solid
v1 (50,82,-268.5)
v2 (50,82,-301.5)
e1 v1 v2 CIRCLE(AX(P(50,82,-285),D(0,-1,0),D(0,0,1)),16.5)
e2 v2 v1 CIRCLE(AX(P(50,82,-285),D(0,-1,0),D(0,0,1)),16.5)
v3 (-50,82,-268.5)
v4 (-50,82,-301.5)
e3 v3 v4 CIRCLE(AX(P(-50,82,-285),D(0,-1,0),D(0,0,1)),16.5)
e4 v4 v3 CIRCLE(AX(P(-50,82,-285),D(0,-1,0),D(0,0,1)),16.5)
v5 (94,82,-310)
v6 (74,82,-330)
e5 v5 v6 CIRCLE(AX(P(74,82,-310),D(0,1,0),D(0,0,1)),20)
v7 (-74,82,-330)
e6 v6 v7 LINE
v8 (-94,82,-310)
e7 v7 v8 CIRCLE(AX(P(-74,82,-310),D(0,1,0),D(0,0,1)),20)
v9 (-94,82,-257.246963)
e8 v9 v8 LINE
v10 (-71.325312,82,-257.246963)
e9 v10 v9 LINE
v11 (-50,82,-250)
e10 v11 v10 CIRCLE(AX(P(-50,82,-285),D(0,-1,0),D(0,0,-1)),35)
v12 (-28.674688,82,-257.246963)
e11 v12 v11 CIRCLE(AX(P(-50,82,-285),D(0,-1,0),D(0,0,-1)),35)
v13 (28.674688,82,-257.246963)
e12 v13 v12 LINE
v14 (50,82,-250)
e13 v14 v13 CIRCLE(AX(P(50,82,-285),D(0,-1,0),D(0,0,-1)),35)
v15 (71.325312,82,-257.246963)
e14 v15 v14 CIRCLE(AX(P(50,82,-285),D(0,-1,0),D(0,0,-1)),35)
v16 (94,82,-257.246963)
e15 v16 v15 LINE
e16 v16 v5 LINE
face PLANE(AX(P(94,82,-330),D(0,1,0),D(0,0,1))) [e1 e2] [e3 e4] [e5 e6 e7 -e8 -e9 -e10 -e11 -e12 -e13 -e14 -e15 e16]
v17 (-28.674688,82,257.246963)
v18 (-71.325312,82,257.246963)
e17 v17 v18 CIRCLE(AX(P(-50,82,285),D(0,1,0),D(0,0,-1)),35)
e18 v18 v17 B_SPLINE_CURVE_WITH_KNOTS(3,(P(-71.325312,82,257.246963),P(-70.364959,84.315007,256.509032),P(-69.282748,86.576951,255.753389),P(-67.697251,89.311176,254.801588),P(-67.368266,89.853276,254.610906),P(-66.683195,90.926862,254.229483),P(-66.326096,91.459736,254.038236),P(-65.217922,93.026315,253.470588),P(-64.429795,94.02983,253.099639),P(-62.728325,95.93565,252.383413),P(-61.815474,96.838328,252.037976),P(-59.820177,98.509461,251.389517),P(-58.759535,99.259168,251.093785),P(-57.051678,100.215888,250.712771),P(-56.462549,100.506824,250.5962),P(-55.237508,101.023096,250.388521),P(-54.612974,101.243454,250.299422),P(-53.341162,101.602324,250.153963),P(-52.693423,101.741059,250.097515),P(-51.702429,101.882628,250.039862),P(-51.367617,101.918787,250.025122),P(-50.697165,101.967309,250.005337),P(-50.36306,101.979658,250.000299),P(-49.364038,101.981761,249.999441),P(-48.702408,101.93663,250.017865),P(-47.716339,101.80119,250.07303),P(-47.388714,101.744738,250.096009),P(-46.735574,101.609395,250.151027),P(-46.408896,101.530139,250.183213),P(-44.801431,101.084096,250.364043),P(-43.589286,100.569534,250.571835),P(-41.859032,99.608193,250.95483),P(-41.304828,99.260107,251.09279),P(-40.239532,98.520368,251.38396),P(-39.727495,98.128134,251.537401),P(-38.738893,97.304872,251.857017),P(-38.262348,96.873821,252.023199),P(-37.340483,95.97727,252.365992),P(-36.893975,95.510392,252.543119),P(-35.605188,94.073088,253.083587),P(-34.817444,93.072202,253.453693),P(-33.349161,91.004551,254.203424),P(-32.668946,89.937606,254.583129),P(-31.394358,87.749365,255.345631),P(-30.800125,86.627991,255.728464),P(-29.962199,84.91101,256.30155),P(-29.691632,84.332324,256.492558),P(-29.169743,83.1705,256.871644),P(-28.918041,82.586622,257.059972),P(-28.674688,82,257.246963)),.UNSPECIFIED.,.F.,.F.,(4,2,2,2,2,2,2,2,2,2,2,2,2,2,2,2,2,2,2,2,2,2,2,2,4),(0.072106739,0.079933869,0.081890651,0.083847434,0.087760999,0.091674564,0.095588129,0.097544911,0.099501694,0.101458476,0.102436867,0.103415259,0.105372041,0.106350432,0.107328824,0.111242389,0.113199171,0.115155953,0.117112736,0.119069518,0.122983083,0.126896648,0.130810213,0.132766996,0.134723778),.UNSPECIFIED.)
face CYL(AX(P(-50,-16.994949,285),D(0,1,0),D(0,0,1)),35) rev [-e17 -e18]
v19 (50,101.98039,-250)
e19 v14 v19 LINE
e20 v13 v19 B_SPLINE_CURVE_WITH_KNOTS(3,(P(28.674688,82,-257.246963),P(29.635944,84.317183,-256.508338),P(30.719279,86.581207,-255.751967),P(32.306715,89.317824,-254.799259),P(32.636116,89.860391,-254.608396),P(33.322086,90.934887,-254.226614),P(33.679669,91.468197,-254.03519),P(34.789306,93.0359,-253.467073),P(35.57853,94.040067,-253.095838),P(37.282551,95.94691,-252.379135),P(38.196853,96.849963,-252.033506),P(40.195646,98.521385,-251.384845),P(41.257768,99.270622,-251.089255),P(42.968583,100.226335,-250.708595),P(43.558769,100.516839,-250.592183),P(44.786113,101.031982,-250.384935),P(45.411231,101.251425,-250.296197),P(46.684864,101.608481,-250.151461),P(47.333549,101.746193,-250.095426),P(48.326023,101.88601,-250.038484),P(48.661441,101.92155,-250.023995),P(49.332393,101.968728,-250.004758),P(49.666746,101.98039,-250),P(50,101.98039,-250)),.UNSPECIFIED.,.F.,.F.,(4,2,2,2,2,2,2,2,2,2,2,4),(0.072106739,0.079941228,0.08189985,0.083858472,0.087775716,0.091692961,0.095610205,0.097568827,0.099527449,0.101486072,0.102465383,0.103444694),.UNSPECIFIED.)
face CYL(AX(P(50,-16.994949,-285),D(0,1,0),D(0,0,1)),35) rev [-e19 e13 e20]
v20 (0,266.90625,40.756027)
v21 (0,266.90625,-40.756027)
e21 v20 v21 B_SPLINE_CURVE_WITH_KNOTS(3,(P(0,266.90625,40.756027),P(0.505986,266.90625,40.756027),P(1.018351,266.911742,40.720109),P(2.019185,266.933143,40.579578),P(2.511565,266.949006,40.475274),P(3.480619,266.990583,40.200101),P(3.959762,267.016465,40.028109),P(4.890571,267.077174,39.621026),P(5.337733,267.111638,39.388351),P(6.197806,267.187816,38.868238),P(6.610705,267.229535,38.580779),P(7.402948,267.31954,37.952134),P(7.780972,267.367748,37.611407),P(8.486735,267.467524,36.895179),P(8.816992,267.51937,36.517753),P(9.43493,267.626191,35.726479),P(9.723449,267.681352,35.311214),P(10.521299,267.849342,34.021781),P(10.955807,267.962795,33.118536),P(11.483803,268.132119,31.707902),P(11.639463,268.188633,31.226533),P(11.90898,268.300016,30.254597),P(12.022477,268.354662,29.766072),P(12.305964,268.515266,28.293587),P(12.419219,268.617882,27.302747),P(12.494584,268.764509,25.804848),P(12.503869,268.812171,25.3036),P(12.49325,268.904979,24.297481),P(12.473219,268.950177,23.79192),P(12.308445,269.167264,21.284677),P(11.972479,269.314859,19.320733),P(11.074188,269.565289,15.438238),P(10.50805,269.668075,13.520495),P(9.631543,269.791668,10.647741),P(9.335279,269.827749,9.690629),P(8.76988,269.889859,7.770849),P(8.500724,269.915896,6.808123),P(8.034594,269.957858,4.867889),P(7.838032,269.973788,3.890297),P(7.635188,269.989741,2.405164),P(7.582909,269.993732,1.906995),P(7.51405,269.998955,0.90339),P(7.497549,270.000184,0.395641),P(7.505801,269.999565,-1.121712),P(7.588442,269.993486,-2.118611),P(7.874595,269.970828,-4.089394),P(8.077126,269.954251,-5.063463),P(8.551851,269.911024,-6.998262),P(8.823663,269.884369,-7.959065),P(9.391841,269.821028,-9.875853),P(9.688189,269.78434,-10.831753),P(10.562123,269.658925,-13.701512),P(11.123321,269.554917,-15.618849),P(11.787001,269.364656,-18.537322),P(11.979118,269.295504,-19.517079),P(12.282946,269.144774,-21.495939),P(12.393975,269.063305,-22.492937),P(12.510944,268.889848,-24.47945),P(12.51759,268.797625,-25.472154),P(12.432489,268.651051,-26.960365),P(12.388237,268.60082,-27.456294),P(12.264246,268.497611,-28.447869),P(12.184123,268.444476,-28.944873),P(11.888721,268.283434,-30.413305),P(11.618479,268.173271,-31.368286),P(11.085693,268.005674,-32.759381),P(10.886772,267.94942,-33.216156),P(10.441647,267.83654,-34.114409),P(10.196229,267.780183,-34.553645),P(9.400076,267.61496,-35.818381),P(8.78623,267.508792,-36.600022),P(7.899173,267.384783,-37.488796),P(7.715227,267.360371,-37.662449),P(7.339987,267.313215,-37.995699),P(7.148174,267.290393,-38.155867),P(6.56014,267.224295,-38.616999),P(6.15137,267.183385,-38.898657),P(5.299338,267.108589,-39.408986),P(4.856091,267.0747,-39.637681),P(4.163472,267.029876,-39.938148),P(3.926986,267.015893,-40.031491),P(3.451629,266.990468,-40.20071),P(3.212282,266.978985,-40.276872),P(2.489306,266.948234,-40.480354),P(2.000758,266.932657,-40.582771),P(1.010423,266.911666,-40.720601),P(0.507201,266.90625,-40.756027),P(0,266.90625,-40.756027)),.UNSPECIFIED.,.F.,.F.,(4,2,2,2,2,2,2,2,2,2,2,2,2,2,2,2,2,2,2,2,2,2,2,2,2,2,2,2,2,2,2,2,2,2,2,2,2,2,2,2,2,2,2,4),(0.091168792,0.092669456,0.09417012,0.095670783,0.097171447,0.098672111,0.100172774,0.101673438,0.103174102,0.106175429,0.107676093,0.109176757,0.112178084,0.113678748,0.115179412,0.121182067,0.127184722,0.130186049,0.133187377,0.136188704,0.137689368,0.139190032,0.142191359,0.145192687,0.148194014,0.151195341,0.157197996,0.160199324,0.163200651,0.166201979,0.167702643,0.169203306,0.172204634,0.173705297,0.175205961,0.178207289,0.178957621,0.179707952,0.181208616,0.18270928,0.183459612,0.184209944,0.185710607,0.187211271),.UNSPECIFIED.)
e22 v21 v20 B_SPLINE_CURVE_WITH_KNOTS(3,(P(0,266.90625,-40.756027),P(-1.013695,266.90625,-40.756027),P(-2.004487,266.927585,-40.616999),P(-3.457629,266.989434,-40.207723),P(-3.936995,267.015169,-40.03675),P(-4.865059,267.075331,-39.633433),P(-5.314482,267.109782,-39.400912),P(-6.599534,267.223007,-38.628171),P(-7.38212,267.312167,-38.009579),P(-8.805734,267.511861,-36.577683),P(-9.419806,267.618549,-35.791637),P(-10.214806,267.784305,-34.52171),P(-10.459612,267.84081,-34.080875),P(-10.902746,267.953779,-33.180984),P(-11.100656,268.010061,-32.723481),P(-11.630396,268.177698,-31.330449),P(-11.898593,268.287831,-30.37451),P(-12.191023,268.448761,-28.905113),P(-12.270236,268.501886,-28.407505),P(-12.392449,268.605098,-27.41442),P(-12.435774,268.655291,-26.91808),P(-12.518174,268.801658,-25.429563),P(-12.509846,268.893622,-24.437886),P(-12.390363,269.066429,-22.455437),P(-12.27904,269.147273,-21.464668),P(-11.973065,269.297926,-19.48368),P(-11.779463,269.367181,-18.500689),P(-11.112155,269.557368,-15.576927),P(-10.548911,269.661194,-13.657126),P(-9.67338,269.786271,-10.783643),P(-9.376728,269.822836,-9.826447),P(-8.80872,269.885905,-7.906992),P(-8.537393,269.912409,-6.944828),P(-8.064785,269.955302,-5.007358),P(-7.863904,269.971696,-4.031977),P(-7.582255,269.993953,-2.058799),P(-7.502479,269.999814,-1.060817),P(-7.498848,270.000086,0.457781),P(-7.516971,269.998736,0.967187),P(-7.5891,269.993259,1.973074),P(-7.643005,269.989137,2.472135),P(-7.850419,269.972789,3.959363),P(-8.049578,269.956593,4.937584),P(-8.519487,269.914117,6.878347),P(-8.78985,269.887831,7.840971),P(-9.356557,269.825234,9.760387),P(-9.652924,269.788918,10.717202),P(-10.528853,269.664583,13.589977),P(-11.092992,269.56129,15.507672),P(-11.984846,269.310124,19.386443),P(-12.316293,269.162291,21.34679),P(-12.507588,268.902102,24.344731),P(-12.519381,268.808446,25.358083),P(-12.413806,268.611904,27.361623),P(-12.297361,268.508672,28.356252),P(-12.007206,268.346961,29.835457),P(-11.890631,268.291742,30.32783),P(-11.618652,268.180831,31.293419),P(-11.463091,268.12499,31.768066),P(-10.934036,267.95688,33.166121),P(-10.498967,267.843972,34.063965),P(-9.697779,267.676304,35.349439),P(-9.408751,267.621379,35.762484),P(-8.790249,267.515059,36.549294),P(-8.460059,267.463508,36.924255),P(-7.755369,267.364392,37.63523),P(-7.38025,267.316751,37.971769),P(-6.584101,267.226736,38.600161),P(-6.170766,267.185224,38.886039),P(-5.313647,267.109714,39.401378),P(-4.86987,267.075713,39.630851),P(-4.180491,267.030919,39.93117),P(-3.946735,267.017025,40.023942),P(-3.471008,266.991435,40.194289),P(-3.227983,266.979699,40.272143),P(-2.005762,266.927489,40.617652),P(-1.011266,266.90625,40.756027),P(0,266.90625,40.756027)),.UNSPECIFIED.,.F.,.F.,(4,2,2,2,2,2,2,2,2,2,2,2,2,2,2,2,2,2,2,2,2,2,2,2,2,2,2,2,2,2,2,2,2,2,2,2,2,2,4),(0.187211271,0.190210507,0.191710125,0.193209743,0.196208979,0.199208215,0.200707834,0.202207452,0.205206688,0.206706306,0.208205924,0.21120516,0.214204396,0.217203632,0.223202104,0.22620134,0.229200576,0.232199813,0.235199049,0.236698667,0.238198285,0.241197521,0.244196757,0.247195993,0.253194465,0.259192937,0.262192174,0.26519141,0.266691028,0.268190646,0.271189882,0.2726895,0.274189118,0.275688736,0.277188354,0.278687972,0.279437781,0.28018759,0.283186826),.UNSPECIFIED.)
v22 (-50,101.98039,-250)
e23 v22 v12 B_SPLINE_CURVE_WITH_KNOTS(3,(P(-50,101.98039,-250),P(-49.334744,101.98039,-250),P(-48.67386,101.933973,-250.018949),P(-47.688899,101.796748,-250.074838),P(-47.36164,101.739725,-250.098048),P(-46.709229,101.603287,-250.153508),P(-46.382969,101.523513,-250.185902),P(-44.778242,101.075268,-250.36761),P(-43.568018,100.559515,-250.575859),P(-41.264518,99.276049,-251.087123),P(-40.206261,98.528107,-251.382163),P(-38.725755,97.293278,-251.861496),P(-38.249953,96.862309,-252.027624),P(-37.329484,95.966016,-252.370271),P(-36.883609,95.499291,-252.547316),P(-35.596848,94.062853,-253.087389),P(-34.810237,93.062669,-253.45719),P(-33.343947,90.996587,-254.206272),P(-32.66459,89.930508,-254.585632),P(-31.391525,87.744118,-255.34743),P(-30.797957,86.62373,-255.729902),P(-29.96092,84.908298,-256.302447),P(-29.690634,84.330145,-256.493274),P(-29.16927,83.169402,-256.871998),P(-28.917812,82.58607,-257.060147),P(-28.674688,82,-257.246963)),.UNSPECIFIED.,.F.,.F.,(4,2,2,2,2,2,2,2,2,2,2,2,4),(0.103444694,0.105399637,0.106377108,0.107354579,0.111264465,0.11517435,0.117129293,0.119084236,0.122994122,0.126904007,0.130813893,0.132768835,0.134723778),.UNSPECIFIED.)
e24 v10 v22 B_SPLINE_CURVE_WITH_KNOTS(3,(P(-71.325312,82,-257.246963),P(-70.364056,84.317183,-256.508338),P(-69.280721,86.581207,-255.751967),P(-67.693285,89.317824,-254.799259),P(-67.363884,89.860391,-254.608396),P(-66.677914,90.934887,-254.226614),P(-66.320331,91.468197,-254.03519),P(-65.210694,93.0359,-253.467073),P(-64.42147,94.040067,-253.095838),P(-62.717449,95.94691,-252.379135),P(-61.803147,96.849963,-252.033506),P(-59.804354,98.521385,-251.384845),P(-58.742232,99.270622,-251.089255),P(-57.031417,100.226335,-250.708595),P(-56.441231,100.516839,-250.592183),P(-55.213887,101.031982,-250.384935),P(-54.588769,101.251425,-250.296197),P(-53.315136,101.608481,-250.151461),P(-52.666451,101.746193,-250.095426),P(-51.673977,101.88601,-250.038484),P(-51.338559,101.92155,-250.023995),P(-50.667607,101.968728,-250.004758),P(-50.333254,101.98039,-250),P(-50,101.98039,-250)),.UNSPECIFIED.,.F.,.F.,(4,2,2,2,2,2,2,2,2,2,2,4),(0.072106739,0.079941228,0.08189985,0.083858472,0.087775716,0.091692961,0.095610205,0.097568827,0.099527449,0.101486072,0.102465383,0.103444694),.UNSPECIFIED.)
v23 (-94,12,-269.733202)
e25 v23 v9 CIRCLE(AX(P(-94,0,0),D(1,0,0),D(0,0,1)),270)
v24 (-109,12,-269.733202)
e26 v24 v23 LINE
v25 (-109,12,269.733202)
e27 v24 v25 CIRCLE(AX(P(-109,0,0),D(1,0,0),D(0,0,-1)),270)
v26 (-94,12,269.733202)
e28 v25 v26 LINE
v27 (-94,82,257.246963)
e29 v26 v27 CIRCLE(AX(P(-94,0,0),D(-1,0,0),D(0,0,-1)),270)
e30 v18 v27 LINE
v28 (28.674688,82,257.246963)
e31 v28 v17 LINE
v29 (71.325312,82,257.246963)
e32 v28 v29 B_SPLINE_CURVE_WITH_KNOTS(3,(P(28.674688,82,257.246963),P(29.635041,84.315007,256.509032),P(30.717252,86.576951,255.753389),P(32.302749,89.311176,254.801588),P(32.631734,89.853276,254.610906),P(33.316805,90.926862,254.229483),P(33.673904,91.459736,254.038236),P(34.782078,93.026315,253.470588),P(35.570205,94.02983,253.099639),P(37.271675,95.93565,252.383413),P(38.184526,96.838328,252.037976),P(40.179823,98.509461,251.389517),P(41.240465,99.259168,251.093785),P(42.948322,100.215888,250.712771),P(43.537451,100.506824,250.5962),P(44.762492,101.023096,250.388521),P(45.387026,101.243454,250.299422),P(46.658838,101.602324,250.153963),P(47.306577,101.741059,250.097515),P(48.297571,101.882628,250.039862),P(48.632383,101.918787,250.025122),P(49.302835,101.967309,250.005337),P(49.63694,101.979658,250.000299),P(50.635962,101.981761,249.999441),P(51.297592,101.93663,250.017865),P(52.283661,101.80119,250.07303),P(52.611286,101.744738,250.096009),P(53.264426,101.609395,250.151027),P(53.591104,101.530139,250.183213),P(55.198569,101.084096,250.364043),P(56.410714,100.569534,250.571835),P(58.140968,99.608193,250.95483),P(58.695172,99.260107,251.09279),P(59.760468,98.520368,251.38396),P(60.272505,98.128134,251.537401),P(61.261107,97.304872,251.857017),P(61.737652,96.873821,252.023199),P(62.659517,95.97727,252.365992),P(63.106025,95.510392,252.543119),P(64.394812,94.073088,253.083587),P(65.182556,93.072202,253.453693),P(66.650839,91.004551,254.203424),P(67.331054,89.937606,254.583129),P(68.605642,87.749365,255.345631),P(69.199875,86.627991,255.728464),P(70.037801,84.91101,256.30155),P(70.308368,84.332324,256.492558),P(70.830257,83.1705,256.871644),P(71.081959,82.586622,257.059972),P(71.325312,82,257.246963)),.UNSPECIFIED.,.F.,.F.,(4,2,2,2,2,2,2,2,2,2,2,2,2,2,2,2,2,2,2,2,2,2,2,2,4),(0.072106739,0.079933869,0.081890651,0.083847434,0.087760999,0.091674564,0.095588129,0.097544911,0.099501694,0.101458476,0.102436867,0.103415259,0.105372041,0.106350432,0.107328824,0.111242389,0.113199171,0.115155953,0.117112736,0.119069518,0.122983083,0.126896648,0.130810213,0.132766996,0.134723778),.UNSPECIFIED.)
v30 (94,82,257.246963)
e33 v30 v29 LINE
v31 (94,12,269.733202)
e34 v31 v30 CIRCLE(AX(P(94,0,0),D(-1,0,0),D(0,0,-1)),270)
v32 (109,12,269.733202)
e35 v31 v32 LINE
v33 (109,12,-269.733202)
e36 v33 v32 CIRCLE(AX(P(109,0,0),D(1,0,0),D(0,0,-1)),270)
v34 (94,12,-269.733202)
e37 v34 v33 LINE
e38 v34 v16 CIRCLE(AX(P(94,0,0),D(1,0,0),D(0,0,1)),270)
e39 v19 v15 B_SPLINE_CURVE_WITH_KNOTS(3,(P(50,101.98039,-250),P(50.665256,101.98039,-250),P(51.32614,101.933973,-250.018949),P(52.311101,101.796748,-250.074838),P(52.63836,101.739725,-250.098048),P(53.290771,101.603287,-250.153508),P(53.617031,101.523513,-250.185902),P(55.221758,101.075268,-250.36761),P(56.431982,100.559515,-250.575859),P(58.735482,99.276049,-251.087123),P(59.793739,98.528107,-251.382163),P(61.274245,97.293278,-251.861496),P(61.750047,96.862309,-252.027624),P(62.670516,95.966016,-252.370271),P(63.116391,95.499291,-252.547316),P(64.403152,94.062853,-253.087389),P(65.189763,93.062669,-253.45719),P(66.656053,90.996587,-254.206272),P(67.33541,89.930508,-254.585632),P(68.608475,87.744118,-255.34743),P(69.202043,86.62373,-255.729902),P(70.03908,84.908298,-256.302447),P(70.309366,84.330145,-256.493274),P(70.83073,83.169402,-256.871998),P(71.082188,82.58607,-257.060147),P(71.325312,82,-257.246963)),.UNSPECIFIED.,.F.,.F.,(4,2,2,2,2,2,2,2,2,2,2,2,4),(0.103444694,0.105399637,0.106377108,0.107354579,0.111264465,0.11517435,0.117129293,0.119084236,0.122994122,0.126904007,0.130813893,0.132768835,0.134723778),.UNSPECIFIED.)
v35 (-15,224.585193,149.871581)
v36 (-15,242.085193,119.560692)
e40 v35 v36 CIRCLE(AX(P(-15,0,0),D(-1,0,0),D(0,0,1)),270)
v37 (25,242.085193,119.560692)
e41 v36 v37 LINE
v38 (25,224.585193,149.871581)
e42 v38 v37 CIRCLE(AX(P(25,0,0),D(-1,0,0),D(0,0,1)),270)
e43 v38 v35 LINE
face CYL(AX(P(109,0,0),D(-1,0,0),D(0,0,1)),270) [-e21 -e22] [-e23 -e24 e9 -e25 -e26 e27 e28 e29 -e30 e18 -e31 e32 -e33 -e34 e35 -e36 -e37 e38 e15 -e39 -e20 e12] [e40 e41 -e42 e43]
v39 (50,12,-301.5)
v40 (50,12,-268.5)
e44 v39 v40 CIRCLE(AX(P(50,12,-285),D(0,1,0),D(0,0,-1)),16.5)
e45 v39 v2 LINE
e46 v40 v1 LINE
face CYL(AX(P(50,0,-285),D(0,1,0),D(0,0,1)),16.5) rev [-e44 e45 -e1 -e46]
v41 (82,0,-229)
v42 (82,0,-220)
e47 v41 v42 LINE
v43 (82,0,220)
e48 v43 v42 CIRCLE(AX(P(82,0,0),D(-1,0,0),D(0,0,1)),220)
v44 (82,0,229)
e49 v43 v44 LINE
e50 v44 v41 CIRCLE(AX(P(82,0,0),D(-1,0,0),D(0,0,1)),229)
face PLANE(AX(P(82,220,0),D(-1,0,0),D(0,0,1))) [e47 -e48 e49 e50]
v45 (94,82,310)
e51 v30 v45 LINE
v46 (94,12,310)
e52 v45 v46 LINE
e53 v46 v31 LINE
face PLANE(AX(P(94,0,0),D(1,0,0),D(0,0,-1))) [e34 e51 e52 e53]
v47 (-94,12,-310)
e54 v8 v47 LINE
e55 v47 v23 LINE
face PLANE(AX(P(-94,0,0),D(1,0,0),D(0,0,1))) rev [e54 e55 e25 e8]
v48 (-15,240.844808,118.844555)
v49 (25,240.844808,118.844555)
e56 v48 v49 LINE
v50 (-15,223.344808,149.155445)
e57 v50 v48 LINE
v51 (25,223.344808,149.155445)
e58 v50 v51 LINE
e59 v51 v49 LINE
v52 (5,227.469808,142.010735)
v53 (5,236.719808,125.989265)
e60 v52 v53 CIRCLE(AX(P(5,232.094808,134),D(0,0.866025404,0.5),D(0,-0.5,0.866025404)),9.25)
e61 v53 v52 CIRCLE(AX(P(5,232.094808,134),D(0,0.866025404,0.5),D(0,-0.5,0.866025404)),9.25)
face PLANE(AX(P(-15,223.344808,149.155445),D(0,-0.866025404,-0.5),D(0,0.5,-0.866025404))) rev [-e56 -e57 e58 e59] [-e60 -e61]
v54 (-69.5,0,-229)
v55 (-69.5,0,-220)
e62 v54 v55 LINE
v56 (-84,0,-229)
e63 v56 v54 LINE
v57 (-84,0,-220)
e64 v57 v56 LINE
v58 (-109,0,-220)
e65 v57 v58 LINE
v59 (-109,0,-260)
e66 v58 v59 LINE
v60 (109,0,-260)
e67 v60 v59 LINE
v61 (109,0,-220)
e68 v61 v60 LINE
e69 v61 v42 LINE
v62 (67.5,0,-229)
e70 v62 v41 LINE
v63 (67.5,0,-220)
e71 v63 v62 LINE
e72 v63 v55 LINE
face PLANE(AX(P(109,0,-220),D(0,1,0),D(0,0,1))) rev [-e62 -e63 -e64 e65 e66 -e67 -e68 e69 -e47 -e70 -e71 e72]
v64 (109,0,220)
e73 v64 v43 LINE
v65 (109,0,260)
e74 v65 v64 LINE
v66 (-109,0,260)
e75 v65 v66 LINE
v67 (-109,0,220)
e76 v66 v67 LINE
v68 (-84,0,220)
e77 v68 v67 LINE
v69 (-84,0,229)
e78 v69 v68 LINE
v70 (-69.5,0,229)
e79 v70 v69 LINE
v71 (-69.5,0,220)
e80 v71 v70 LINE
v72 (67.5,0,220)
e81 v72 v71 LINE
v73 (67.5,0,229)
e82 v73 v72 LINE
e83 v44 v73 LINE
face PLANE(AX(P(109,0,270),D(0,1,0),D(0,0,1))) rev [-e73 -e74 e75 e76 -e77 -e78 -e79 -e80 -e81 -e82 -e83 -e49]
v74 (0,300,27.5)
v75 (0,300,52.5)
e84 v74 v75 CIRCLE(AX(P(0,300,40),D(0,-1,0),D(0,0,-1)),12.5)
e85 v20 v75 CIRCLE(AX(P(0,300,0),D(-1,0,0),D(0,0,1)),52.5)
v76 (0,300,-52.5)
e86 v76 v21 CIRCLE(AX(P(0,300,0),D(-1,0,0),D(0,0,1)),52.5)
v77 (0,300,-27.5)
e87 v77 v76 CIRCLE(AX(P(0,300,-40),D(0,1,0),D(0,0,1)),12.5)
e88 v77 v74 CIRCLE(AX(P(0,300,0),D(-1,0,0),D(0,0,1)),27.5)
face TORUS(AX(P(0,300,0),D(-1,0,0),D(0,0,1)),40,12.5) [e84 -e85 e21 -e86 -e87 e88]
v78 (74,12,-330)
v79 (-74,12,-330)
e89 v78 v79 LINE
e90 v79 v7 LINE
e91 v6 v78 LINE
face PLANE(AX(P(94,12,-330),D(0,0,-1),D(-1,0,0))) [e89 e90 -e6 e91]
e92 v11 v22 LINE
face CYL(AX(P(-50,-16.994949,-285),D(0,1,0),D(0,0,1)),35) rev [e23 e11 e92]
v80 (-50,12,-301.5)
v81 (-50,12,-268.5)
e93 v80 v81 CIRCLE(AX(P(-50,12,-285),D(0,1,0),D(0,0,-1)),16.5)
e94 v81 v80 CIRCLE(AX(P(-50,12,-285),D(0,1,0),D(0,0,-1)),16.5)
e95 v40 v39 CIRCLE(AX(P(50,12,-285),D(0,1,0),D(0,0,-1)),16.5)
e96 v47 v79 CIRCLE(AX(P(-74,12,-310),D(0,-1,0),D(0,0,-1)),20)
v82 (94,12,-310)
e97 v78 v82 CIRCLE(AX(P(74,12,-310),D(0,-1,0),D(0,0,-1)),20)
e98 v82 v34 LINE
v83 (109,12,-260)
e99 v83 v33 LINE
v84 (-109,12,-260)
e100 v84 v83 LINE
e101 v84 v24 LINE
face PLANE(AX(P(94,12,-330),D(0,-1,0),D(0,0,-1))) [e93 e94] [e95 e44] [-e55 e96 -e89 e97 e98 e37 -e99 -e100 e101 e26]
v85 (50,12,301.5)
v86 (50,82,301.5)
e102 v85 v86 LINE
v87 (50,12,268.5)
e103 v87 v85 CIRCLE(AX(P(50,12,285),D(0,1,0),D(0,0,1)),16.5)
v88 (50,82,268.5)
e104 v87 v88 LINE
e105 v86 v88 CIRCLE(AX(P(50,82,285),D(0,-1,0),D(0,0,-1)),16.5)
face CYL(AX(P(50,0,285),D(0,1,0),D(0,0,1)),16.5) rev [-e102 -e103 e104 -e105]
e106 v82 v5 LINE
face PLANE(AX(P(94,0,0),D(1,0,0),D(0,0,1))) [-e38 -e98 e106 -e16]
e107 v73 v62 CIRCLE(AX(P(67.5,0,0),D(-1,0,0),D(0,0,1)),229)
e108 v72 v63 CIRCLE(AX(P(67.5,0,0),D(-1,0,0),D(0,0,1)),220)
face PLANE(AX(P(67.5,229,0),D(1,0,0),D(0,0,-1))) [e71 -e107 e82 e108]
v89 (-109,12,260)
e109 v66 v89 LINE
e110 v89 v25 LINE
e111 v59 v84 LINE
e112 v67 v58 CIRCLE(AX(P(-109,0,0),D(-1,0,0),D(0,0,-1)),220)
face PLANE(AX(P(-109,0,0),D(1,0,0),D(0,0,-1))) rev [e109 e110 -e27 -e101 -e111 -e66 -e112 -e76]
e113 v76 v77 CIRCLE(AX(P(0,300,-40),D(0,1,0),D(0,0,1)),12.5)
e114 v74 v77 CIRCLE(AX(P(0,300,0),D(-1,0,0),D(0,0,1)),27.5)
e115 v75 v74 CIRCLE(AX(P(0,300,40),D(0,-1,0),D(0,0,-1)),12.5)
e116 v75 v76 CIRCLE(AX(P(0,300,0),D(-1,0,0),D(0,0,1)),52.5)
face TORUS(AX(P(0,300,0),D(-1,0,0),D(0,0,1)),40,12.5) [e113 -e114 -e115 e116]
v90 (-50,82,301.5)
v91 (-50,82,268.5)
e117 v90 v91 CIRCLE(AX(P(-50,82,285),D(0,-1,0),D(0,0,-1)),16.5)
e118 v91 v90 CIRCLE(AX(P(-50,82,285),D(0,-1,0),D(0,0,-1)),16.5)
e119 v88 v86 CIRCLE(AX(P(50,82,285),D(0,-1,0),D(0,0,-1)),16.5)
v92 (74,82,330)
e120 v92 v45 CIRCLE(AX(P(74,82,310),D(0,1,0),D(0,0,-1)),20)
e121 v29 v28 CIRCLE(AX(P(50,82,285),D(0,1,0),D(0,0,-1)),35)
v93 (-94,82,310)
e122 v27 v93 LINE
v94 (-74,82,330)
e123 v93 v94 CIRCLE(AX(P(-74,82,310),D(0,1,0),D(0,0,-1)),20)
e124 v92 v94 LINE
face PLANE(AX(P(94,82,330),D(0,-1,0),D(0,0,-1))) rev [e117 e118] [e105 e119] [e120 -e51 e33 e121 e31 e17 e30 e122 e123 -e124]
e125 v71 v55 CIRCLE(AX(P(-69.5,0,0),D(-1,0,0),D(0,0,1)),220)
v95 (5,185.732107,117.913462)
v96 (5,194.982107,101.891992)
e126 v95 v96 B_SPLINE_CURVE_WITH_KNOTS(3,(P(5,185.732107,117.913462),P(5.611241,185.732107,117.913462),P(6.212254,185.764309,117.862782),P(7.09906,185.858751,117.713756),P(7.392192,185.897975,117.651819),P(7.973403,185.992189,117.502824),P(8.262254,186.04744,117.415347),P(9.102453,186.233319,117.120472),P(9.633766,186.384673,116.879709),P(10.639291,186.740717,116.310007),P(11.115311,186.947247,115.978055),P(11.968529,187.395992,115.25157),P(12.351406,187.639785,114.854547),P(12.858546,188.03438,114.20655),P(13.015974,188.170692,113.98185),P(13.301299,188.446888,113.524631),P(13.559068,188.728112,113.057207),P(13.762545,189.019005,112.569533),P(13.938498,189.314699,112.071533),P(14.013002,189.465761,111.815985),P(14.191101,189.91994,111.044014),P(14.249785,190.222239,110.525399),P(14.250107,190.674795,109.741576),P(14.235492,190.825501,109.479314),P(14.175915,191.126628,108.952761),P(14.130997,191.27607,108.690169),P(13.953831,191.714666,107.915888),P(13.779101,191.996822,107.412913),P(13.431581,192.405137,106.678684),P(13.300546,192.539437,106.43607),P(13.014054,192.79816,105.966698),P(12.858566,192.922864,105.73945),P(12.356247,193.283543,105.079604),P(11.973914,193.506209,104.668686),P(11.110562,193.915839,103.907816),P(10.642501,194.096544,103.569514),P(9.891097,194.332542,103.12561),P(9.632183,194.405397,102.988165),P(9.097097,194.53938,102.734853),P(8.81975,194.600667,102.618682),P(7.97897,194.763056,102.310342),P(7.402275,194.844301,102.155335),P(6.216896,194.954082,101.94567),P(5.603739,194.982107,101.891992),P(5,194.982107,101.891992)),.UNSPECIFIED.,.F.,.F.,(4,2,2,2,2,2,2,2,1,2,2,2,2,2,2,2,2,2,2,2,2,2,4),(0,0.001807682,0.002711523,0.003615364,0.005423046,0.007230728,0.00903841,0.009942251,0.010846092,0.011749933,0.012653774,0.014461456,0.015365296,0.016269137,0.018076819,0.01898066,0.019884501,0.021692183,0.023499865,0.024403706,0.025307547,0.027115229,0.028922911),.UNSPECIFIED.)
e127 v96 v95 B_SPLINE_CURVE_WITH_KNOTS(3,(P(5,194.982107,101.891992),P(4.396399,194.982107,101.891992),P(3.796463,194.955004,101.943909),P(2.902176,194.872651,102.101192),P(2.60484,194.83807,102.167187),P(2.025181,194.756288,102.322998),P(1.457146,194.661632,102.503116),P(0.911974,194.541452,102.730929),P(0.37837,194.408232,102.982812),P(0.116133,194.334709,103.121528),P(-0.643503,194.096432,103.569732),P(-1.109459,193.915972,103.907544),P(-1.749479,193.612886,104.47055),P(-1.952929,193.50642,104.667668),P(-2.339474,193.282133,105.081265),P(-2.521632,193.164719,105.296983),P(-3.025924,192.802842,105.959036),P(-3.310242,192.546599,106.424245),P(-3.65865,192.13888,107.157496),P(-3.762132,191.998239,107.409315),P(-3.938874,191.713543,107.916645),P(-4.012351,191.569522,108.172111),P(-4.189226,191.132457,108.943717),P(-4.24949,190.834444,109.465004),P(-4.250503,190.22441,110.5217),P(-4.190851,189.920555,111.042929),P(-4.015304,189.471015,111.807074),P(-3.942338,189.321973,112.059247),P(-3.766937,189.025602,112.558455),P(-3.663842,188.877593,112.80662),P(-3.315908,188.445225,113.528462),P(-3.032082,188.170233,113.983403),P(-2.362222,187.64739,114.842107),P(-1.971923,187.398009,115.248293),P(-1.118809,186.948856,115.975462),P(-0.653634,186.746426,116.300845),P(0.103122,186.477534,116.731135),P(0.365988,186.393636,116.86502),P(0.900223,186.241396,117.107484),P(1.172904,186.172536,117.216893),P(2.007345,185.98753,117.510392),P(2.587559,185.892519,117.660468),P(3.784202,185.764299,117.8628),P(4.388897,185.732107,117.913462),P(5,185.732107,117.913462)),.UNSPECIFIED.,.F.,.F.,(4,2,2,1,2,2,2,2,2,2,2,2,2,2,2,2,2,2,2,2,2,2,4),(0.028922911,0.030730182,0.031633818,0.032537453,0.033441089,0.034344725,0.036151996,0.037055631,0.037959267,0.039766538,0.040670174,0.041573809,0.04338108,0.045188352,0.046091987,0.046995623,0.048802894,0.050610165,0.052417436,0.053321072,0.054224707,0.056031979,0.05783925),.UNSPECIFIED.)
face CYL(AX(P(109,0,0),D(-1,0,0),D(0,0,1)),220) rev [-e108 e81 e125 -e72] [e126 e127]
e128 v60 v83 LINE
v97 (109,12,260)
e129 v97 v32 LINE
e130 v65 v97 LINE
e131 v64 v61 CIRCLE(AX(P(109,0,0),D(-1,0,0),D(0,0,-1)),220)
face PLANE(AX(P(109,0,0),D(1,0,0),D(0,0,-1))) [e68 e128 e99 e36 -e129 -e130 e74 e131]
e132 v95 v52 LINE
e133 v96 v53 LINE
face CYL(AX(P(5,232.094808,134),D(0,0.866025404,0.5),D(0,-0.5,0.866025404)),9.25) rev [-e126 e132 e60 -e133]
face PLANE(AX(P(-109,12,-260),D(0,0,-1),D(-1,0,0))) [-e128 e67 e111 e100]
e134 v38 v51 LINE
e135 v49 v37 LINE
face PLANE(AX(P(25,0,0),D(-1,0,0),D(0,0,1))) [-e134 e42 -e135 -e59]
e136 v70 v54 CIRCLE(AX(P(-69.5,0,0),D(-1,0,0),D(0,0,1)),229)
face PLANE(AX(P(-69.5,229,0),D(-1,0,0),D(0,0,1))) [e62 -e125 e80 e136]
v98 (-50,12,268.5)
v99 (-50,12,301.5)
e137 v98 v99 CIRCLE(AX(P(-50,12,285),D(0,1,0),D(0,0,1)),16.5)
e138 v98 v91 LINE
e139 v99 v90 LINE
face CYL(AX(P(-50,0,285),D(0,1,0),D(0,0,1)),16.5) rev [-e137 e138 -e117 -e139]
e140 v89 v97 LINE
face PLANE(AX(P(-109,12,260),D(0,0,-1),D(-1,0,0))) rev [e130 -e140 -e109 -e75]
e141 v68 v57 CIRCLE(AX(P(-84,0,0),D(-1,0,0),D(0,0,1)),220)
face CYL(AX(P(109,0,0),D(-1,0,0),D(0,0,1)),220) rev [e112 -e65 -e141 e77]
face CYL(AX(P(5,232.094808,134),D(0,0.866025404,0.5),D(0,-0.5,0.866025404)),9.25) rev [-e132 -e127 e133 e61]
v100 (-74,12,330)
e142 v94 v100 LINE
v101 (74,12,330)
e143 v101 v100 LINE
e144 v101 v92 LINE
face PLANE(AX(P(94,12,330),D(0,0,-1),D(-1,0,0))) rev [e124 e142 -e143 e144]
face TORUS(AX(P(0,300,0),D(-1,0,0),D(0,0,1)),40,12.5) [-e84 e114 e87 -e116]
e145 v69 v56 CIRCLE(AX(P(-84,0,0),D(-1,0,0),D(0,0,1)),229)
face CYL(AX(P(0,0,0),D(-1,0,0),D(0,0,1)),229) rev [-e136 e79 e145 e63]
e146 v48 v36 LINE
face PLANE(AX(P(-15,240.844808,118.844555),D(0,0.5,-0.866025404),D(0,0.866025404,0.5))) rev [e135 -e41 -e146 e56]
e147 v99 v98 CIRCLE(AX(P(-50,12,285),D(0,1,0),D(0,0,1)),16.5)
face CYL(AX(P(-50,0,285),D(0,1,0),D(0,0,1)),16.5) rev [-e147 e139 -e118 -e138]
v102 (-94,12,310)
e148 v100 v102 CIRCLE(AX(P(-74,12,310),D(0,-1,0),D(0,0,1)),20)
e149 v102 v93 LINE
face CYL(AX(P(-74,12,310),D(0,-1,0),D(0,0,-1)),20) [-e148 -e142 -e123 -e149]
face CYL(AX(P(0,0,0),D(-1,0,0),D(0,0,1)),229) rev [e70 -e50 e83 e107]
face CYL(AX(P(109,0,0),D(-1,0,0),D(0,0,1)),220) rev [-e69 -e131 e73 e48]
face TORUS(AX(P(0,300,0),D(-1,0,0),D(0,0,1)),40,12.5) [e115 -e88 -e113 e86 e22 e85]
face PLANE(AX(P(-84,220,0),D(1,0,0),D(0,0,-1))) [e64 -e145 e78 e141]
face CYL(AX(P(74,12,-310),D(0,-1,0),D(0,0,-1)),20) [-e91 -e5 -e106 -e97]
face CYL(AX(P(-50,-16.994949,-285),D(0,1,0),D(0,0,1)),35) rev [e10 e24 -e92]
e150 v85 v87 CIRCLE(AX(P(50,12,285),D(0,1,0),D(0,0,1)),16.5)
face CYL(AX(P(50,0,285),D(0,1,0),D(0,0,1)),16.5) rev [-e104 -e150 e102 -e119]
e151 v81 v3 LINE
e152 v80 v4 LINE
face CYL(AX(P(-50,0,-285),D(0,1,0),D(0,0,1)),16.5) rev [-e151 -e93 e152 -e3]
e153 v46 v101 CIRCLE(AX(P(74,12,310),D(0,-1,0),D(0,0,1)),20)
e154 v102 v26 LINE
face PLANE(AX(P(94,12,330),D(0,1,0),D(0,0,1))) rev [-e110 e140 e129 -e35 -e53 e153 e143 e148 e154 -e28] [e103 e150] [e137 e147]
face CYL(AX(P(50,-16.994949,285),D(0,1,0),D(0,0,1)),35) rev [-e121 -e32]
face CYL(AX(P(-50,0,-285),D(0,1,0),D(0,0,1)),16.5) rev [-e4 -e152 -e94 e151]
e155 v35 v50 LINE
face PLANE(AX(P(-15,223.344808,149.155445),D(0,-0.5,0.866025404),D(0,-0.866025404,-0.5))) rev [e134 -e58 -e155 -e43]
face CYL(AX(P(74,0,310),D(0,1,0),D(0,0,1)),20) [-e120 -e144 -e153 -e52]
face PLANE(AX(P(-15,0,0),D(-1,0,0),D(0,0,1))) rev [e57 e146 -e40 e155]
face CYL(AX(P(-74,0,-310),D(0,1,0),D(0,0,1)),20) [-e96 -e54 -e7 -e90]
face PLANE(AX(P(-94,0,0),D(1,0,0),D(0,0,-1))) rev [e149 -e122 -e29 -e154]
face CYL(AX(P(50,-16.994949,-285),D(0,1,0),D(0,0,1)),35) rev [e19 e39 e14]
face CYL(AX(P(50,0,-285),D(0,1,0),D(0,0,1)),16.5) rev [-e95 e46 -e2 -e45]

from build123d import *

# Parameters (mm, degrees)
BOSS_EXTRUDE2_DEPTH    = 109
BOSS_EXTRUDE3_DEPTH    = 94
SKETCH5_R              = 16.5
CUT_EXTRUDE1_DEPTH     = 396.126562003
CUT_EXTRUDE2_START     = 82
SKETCH6_R              = 35
CUT_EXTRUDE2_DEPTH     = 19.98039
SKETCH7_W              = 39.278789695
SKETCH7_H              = 17.735547429
CUT_EXTRUDE3_DEPTH     = 441.092035915
FILLET1_R              = 20
FILLET1_OF_MIRROR1_R   = 20
SKETCH8_W              = 14.5
SKETCH8_H              = 9
SKETCH9_R              = 12.5
CUT_EXTRUDE4_START     = 5
CUT_EXTRUDE4_DEPTH     = 20
M20X1_5_TAPPED_HOLE1_D = 18.5


with BuildPart() as part:
    # Sketch1 → Boss-Extrude2 (new, symmetric)
    with BuildSketch(Plane(origin=(0, 0, 0), x_dir=(0, 0, -1), z_dir=(1, 0, 0))):
        with BuildLine():
            Line((-270, 0), (-220, 0))
            ThreePointArc((-220, 0), (0, 220), (220, 0))
            Line((220, 0), (270, 0))
            ThreePointArc((270, 0), (0, 270), (-270, 0))
        make_face()
    extrude(amount=BOSS_EXTRUDE2_DEPTH, both=True)

    # Sketch4 → Boss-Extrude3 (add, symmetric)
    with BuildSketch(Plane(origin=(0, 0, 0), x_dir=(0, 0, -1), z_dir=(1, 0, 0))):
        with BuildLine():
            Line((-330, 12), (-269.733201516, 12))
            ThreePointArc((-269.733201516, 12), (-265.804483526, 47.41283094), (-257.246963053, 82))
            Line((-257.246963053, 82), (-330, 82))
            Line((-330, 82), (-330, 12))
        make_face()
    boss_extrude3 = extrude(amount=BOSS_EXTRUDE3_DEPTH, both=True)

    # Sketch5 → Cut-Extrude1 (cut, symmetric)
    with BuildSketch(Plane(origin=(0, 82, 0), x_dir=(1, 0, 0), z_dir=(0, 1, 0))):
        with Locations(Location((50, -285, 0), (0, 0, 65.380022671))):
            Circle(SKETCH5_R)
        with Locations(Location((-50, -285, 0), (0, 0, 65.380022671))):
            Circle(SKETCH5_R)
    cut_extrude1 = extrude(amount=CUT_EXTRUDE1_DEPTH, both=True, mode=Mode.SUBTRACT)

    # Sketch6 → Cut-Extrude2 (cut)
    with BuildSketch(Plane(origin=(0, 0, 0), x_dir=(1, 0, 0), z_dir=(0, 1, 0)).offset(CUT_EXTRUDE2_START)):
        with Locations((-50, -285)):
            Circle(SKETCH6_R)
        with Locations((50, -285)):
            Circle(SKETCH6_R)
    cut_extrude2 = extrude(amount=CUT_EXTRUDE2_DEPTH, mode=Mode.SUBTRACT)

    # Sketch7 → Cut-Extrude3 (cut, symmetric)
    with BuildSketch(Plane(origin=(0, 0, 0), x_dir=(0, 0, -1), z_dir=(1, 0, 0))):
        with Locations((-279.639394848, 3.132226285)):
            Rectangle(SKETCH7_W, SKETCH7_H)
    cut_extrude3 = extrude(amount=CUT_EXTRUDE3_DEPTH, both=True, mode=Mode.SUBTRACT)

    # Fillet1
    fillet1_edges = [part.edges().sort_by_distance(p)[0] for p in [
        (-94, 47, 330),
        (94, 47, 330),
    ]]
    fillet(fillet1_edges, radius=FILLET1_R)

    # Mirror1: Boss-Extrude3, Cut-Extrude1, Cut-Extrude2, Cut-Extrude3 across plane
    add(boss_extrude3.mirror(Plane.XY))
    add(cut_extrude1.mirror(Plane.XY), mode=Mode.SUBTRACT)
    add(cut_extrude2.mirror(Plane.XY), mode=Mode.SUBTRACT)
    add(cut_extrude3.mirror(Plane.XY), mode=Mode.SUBTRACT)

    # Fillet1 of Mirror1
    fillet1_of_mirror1_edges = [part.edges().sort_by_distance(p)[0] for p in [
        (-94, 47, -330),
        (94, 47, -330),
    ]]
    fillet(fillet1_of_mirror1_edges, radius=FILLET1_OF_MIRROR1_R)

    # Sketch8 → Cut-Revolve1 (revolve, cut)
    with BuildSketch(Plane.XY):
        with Locations((-76.75, 224.5)):
            Rectangle(SKETCH8_W, SKETCH8_H)
        with Locations((74.75, 224.5)):
            Rectangle(SKETCH8_W, SKETCH8_H)
    revolve(axis=Axis((0, 0, 0), (1, 0, 0)), mode=Mode.SUBTRACT)

    # Sketch9 → Revolve1 (revolve)
    with BuildSketch(Plane.XY, mode=Mode.PRIVATE) as revolve1_sk:
        with Locations((0, 340)):
            Circle(SKETCH9_R)
    revolve(revolve1_sk.sketch.rotate(Axis((0, 300, 0), (1, 0, 0)), 340.461761532), axis=Axis((0, 300, 0), (1, 0, 0)))

    # Sketch10 → Cut-Extrude4 (cut, symmetric)
    with BuildSketch(Plane(origin=(0, 0, 0), x_dir=(0, 0, -1), z_dir=(1, 0, 0)).offset(CUT_EXTRUDE4_START)):
        Polygon((-149.155444566, 223.344808214), (-118.844555434, 240.844808214), (-120.844555434, 244.308909829), (-151.155444566, 226.808909829), align=None)
    extrude(amount=CUT_EXTRUDE4_DEPTH, both=True, mode=Mode.SUBTRACT)

    # M20x1.5 Tapped Hole1 (through all)
    with Locations(Plane(origin=(5, 232.094808214, 134), x_dir=(0, -0.5, 0.866025403784), z_dir=(0, 0.866025403784, 0.5))):
        with Locations((0, 0)):
            Hole(M20X1_5_TAPPED_HOLE1_D / 2)


solid = part.part
